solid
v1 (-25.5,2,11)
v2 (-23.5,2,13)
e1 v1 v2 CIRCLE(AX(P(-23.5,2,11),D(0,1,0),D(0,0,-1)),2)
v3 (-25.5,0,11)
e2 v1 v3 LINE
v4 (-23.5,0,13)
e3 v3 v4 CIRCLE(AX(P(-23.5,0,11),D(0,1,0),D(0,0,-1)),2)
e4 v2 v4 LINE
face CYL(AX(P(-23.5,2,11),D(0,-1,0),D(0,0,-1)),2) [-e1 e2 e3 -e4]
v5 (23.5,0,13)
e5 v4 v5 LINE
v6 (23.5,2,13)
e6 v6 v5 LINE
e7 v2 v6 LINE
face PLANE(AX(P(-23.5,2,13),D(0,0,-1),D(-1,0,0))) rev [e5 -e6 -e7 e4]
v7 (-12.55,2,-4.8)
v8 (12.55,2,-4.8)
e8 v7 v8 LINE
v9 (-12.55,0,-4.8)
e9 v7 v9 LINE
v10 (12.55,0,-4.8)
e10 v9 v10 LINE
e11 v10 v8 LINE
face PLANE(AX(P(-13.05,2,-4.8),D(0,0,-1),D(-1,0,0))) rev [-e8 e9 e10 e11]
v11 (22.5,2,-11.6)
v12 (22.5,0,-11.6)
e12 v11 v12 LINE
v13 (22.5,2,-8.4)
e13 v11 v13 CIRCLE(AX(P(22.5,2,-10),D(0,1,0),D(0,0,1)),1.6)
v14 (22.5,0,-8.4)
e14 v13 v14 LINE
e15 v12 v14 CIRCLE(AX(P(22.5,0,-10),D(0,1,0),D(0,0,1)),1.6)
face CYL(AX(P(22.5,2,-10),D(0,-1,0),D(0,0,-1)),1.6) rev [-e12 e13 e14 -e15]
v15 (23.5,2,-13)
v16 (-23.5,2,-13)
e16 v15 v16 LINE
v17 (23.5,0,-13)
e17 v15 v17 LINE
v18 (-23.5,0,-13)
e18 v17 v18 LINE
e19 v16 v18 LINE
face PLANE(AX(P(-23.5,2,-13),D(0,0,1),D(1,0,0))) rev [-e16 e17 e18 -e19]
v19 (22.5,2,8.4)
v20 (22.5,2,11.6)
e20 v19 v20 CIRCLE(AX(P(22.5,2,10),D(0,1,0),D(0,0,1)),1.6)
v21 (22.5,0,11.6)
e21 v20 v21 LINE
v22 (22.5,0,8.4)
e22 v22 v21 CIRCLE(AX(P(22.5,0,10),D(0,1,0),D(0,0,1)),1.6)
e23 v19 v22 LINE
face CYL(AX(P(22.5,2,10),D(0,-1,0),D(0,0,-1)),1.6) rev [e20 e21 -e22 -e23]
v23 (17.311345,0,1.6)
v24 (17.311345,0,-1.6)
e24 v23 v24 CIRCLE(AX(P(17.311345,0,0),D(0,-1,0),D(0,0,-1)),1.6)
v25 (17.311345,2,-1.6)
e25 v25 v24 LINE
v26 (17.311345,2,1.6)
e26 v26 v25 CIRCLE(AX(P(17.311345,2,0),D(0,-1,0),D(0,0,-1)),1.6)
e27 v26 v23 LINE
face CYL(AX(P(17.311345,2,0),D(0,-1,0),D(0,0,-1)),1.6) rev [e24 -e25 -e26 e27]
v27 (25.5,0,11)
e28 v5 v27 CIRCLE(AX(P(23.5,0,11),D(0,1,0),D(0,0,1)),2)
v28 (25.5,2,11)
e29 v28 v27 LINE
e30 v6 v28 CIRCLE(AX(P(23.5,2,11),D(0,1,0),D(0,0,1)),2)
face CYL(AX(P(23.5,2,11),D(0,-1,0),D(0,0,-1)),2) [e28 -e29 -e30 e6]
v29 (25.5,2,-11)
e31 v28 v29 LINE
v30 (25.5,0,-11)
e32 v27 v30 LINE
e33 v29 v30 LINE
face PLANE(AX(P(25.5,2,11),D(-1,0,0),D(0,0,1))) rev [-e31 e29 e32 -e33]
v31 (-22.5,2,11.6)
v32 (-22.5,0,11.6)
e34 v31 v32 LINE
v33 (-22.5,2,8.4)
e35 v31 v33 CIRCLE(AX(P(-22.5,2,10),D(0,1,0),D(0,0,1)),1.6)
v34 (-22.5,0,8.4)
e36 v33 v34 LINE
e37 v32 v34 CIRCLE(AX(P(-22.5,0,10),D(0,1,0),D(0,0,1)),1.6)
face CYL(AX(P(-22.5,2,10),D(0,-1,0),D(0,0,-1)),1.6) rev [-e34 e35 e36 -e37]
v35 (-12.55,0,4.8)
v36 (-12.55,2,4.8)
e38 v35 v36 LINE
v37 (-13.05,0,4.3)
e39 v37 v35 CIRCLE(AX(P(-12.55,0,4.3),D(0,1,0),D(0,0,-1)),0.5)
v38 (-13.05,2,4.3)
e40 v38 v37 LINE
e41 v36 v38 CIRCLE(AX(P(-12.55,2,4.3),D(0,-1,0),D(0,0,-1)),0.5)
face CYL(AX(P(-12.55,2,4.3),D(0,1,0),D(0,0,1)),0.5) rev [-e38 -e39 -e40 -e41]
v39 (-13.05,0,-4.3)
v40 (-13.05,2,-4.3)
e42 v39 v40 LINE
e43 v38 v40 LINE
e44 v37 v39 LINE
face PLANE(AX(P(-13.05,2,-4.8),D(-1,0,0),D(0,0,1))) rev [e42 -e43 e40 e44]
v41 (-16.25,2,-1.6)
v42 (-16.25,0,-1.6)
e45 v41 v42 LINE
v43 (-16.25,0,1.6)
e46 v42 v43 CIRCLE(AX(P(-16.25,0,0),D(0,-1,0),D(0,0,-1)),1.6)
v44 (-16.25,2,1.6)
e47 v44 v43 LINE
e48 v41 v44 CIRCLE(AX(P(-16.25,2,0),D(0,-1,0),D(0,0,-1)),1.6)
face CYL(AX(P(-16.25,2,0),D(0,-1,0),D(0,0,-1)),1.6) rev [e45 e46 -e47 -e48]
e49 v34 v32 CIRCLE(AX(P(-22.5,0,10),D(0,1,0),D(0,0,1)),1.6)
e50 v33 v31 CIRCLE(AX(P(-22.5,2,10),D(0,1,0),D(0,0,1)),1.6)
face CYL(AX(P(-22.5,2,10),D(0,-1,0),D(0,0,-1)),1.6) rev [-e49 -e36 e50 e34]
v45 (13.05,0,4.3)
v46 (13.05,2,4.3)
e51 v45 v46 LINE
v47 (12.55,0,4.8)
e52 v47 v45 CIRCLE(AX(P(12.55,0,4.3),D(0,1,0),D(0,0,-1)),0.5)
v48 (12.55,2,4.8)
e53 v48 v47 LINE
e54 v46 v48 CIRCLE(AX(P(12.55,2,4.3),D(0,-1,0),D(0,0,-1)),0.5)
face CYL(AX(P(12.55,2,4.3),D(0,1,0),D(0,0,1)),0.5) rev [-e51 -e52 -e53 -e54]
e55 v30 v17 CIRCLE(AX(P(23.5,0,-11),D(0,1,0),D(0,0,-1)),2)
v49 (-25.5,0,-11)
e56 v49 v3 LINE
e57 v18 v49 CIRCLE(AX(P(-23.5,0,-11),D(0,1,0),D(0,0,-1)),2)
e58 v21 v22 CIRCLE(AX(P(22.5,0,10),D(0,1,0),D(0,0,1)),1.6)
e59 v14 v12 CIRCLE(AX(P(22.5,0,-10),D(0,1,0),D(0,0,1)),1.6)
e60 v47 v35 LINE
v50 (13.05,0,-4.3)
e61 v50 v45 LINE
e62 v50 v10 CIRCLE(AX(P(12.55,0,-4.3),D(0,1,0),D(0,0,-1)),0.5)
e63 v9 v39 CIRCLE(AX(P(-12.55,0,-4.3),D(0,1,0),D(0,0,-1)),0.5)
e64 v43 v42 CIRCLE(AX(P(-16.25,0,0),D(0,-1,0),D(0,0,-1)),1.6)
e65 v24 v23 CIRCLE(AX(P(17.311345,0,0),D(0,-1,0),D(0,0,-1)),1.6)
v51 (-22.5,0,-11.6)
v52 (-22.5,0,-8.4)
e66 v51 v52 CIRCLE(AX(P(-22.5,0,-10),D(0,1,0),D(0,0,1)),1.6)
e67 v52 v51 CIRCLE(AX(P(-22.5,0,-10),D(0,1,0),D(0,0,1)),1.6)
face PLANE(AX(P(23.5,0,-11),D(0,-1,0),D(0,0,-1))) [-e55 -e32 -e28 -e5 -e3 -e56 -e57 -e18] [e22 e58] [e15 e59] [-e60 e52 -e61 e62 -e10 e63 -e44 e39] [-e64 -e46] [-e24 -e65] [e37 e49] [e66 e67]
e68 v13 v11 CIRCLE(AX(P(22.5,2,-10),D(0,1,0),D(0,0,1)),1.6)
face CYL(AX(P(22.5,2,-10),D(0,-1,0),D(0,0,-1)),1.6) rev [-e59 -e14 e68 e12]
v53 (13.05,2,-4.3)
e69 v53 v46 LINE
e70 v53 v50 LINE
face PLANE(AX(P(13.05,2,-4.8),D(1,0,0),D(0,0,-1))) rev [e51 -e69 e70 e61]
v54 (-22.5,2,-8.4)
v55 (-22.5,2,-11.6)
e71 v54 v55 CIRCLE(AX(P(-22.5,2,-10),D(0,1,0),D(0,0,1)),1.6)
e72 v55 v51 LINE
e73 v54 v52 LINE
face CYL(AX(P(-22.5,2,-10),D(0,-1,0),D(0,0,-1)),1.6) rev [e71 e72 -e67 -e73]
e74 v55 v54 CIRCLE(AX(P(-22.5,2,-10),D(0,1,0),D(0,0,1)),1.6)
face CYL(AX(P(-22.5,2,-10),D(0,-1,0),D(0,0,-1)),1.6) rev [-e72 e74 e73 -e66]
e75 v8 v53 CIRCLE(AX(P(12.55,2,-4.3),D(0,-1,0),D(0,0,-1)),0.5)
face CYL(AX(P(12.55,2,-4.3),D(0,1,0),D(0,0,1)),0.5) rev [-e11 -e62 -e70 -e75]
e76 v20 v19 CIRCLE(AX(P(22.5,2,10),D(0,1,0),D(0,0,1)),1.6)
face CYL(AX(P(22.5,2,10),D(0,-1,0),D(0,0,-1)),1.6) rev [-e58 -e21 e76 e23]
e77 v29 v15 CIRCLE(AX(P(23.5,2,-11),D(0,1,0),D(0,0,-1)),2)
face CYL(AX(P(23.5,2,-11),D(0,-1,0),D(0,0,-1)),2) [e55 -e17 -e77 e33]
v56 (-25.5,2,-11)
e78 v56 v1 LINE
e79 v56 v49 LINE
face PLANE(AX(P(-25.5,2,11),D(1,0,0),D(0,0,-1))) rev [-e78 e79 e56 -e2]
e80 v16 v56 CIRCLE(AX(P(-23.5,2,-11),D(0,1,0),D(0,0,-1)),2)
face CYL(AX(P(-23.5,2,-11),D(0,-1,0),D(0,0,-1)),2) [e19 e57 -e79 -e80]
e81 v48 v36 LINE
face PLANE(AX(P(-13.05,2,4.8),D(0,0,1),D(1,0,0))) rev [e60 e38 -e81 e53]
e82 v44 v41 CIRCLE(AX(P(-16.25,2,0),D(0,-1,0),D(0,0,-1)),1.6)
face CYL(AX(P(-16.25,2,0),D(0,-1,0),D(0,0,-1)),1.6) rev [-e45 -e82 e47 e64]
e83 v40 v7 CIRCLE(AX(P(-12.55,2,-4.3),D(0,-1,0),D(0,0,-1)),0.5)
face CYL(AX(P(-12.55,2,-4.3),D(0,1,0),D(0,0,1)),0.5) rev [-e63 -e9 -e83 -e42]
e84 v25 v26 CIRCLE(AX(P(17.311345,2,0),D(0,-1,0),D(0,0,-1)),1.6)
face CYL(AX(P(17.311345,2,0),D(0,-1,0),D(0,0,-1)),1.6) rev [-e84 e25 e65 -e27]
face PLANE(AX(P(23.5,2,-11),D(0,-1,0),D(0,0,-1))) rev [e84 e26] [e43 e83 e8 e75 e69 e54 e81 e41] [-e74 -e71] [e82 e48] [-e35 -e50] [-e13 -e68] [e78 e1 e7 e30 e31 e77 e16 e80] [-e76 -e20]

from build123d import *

# Parameters (mm, degrees)
SKETCH1_R           = 1.6
BOSS_EXTRUDE1_DEPTH = 2
SKETCH2_R           = 1.6
SKETCH2_W           = 26.1
SKETCH2_H           = 9.6
CUT_EXTRUDE1_DEPTH  = 2
FILLET1_R           = 0.5


with BuildPart() as part:
    # Sketch1 → Boss-Extrude1 (new body)
    with BuildSketch(Plane(origin=(0, 0, 0), x_dir=(1, 0, 0), z_dir=(0, 1, 0))):
        with BuildLine():
            Line((-23.5, -13), (23.5, -13))
            ThreePointArc((23.5, -13), (24.914213562, -12.414213562), (25.5, -11))
            Line((25.5, -11), (25.5, 11))
            ThreePointArc((25.5, 11), (24.914213562, 12.414213562), (23.5, 13))
            Line((23.5, 13), (-23.5, 13))
            ThreePointArc((-23.5, 13), (-24.914213562, 12.414213562), (-25.5, 11))
            Line((-25.5, 11), (-25.5, -11))
            ThreePointArc((-25.5, -11), (-24.914213562, -12.414213562), (-23.5, -13))
        make_face()
        with Locations(Location((-22.5, 10, 0), (0, 0, 270))):
            Circle(SKETCH1_R, mode=Mode.SUBTRACT)
        with Locations(Location((22.5, 10, 0), (0, 0, 270))):
            Circle(SKETCH1_R, mode=Mode.SUBTRACT)
        with Locations(Location((22.5, -10, 0), (0, 0, 270))):
            Circle(SKETCH1_R, mode=Mode.SUBTRACT)
        with Locations(Location((-22.5, -10, 0), (0, 0, 270))):
            Circle(SKETCH1_R, mode=Mode.SUBTRACT)
    extrude(amount=BOSS_EXTRUDE1_DEPTH)

    # Sketch2 → Cut-Extrude1 (cut)
    with BuildSketch(Plane.XZ):
        with Locations(Location((-16.25, 0, 0), (0, 0, 270))):
            Circle(SKETCH2_R)
        with Locations(Location((17.311344744, 0, 0), (0, 0, 270))):
            Circle(SKETCH2_R)
        Rectangle(SKETCH2_W, SKETCH2_H)
    extrude(amount=-CUT_EXTRUDE1_DEPTH, mode=Mode.SUBTRACT)

    # Fillet1
    fillet1_edges = [part.edges().sort_by_distance(p)[0] for p in [
        (13.05, 1, 4.8),
        (13.05, 1, -4.8),
        (-13.05, 1, -4.8),
        (-13.05, 1, 4.8),
    ]]
    fillet(fillet1_edges, radius=FILLET1_R)


solid = part.part
